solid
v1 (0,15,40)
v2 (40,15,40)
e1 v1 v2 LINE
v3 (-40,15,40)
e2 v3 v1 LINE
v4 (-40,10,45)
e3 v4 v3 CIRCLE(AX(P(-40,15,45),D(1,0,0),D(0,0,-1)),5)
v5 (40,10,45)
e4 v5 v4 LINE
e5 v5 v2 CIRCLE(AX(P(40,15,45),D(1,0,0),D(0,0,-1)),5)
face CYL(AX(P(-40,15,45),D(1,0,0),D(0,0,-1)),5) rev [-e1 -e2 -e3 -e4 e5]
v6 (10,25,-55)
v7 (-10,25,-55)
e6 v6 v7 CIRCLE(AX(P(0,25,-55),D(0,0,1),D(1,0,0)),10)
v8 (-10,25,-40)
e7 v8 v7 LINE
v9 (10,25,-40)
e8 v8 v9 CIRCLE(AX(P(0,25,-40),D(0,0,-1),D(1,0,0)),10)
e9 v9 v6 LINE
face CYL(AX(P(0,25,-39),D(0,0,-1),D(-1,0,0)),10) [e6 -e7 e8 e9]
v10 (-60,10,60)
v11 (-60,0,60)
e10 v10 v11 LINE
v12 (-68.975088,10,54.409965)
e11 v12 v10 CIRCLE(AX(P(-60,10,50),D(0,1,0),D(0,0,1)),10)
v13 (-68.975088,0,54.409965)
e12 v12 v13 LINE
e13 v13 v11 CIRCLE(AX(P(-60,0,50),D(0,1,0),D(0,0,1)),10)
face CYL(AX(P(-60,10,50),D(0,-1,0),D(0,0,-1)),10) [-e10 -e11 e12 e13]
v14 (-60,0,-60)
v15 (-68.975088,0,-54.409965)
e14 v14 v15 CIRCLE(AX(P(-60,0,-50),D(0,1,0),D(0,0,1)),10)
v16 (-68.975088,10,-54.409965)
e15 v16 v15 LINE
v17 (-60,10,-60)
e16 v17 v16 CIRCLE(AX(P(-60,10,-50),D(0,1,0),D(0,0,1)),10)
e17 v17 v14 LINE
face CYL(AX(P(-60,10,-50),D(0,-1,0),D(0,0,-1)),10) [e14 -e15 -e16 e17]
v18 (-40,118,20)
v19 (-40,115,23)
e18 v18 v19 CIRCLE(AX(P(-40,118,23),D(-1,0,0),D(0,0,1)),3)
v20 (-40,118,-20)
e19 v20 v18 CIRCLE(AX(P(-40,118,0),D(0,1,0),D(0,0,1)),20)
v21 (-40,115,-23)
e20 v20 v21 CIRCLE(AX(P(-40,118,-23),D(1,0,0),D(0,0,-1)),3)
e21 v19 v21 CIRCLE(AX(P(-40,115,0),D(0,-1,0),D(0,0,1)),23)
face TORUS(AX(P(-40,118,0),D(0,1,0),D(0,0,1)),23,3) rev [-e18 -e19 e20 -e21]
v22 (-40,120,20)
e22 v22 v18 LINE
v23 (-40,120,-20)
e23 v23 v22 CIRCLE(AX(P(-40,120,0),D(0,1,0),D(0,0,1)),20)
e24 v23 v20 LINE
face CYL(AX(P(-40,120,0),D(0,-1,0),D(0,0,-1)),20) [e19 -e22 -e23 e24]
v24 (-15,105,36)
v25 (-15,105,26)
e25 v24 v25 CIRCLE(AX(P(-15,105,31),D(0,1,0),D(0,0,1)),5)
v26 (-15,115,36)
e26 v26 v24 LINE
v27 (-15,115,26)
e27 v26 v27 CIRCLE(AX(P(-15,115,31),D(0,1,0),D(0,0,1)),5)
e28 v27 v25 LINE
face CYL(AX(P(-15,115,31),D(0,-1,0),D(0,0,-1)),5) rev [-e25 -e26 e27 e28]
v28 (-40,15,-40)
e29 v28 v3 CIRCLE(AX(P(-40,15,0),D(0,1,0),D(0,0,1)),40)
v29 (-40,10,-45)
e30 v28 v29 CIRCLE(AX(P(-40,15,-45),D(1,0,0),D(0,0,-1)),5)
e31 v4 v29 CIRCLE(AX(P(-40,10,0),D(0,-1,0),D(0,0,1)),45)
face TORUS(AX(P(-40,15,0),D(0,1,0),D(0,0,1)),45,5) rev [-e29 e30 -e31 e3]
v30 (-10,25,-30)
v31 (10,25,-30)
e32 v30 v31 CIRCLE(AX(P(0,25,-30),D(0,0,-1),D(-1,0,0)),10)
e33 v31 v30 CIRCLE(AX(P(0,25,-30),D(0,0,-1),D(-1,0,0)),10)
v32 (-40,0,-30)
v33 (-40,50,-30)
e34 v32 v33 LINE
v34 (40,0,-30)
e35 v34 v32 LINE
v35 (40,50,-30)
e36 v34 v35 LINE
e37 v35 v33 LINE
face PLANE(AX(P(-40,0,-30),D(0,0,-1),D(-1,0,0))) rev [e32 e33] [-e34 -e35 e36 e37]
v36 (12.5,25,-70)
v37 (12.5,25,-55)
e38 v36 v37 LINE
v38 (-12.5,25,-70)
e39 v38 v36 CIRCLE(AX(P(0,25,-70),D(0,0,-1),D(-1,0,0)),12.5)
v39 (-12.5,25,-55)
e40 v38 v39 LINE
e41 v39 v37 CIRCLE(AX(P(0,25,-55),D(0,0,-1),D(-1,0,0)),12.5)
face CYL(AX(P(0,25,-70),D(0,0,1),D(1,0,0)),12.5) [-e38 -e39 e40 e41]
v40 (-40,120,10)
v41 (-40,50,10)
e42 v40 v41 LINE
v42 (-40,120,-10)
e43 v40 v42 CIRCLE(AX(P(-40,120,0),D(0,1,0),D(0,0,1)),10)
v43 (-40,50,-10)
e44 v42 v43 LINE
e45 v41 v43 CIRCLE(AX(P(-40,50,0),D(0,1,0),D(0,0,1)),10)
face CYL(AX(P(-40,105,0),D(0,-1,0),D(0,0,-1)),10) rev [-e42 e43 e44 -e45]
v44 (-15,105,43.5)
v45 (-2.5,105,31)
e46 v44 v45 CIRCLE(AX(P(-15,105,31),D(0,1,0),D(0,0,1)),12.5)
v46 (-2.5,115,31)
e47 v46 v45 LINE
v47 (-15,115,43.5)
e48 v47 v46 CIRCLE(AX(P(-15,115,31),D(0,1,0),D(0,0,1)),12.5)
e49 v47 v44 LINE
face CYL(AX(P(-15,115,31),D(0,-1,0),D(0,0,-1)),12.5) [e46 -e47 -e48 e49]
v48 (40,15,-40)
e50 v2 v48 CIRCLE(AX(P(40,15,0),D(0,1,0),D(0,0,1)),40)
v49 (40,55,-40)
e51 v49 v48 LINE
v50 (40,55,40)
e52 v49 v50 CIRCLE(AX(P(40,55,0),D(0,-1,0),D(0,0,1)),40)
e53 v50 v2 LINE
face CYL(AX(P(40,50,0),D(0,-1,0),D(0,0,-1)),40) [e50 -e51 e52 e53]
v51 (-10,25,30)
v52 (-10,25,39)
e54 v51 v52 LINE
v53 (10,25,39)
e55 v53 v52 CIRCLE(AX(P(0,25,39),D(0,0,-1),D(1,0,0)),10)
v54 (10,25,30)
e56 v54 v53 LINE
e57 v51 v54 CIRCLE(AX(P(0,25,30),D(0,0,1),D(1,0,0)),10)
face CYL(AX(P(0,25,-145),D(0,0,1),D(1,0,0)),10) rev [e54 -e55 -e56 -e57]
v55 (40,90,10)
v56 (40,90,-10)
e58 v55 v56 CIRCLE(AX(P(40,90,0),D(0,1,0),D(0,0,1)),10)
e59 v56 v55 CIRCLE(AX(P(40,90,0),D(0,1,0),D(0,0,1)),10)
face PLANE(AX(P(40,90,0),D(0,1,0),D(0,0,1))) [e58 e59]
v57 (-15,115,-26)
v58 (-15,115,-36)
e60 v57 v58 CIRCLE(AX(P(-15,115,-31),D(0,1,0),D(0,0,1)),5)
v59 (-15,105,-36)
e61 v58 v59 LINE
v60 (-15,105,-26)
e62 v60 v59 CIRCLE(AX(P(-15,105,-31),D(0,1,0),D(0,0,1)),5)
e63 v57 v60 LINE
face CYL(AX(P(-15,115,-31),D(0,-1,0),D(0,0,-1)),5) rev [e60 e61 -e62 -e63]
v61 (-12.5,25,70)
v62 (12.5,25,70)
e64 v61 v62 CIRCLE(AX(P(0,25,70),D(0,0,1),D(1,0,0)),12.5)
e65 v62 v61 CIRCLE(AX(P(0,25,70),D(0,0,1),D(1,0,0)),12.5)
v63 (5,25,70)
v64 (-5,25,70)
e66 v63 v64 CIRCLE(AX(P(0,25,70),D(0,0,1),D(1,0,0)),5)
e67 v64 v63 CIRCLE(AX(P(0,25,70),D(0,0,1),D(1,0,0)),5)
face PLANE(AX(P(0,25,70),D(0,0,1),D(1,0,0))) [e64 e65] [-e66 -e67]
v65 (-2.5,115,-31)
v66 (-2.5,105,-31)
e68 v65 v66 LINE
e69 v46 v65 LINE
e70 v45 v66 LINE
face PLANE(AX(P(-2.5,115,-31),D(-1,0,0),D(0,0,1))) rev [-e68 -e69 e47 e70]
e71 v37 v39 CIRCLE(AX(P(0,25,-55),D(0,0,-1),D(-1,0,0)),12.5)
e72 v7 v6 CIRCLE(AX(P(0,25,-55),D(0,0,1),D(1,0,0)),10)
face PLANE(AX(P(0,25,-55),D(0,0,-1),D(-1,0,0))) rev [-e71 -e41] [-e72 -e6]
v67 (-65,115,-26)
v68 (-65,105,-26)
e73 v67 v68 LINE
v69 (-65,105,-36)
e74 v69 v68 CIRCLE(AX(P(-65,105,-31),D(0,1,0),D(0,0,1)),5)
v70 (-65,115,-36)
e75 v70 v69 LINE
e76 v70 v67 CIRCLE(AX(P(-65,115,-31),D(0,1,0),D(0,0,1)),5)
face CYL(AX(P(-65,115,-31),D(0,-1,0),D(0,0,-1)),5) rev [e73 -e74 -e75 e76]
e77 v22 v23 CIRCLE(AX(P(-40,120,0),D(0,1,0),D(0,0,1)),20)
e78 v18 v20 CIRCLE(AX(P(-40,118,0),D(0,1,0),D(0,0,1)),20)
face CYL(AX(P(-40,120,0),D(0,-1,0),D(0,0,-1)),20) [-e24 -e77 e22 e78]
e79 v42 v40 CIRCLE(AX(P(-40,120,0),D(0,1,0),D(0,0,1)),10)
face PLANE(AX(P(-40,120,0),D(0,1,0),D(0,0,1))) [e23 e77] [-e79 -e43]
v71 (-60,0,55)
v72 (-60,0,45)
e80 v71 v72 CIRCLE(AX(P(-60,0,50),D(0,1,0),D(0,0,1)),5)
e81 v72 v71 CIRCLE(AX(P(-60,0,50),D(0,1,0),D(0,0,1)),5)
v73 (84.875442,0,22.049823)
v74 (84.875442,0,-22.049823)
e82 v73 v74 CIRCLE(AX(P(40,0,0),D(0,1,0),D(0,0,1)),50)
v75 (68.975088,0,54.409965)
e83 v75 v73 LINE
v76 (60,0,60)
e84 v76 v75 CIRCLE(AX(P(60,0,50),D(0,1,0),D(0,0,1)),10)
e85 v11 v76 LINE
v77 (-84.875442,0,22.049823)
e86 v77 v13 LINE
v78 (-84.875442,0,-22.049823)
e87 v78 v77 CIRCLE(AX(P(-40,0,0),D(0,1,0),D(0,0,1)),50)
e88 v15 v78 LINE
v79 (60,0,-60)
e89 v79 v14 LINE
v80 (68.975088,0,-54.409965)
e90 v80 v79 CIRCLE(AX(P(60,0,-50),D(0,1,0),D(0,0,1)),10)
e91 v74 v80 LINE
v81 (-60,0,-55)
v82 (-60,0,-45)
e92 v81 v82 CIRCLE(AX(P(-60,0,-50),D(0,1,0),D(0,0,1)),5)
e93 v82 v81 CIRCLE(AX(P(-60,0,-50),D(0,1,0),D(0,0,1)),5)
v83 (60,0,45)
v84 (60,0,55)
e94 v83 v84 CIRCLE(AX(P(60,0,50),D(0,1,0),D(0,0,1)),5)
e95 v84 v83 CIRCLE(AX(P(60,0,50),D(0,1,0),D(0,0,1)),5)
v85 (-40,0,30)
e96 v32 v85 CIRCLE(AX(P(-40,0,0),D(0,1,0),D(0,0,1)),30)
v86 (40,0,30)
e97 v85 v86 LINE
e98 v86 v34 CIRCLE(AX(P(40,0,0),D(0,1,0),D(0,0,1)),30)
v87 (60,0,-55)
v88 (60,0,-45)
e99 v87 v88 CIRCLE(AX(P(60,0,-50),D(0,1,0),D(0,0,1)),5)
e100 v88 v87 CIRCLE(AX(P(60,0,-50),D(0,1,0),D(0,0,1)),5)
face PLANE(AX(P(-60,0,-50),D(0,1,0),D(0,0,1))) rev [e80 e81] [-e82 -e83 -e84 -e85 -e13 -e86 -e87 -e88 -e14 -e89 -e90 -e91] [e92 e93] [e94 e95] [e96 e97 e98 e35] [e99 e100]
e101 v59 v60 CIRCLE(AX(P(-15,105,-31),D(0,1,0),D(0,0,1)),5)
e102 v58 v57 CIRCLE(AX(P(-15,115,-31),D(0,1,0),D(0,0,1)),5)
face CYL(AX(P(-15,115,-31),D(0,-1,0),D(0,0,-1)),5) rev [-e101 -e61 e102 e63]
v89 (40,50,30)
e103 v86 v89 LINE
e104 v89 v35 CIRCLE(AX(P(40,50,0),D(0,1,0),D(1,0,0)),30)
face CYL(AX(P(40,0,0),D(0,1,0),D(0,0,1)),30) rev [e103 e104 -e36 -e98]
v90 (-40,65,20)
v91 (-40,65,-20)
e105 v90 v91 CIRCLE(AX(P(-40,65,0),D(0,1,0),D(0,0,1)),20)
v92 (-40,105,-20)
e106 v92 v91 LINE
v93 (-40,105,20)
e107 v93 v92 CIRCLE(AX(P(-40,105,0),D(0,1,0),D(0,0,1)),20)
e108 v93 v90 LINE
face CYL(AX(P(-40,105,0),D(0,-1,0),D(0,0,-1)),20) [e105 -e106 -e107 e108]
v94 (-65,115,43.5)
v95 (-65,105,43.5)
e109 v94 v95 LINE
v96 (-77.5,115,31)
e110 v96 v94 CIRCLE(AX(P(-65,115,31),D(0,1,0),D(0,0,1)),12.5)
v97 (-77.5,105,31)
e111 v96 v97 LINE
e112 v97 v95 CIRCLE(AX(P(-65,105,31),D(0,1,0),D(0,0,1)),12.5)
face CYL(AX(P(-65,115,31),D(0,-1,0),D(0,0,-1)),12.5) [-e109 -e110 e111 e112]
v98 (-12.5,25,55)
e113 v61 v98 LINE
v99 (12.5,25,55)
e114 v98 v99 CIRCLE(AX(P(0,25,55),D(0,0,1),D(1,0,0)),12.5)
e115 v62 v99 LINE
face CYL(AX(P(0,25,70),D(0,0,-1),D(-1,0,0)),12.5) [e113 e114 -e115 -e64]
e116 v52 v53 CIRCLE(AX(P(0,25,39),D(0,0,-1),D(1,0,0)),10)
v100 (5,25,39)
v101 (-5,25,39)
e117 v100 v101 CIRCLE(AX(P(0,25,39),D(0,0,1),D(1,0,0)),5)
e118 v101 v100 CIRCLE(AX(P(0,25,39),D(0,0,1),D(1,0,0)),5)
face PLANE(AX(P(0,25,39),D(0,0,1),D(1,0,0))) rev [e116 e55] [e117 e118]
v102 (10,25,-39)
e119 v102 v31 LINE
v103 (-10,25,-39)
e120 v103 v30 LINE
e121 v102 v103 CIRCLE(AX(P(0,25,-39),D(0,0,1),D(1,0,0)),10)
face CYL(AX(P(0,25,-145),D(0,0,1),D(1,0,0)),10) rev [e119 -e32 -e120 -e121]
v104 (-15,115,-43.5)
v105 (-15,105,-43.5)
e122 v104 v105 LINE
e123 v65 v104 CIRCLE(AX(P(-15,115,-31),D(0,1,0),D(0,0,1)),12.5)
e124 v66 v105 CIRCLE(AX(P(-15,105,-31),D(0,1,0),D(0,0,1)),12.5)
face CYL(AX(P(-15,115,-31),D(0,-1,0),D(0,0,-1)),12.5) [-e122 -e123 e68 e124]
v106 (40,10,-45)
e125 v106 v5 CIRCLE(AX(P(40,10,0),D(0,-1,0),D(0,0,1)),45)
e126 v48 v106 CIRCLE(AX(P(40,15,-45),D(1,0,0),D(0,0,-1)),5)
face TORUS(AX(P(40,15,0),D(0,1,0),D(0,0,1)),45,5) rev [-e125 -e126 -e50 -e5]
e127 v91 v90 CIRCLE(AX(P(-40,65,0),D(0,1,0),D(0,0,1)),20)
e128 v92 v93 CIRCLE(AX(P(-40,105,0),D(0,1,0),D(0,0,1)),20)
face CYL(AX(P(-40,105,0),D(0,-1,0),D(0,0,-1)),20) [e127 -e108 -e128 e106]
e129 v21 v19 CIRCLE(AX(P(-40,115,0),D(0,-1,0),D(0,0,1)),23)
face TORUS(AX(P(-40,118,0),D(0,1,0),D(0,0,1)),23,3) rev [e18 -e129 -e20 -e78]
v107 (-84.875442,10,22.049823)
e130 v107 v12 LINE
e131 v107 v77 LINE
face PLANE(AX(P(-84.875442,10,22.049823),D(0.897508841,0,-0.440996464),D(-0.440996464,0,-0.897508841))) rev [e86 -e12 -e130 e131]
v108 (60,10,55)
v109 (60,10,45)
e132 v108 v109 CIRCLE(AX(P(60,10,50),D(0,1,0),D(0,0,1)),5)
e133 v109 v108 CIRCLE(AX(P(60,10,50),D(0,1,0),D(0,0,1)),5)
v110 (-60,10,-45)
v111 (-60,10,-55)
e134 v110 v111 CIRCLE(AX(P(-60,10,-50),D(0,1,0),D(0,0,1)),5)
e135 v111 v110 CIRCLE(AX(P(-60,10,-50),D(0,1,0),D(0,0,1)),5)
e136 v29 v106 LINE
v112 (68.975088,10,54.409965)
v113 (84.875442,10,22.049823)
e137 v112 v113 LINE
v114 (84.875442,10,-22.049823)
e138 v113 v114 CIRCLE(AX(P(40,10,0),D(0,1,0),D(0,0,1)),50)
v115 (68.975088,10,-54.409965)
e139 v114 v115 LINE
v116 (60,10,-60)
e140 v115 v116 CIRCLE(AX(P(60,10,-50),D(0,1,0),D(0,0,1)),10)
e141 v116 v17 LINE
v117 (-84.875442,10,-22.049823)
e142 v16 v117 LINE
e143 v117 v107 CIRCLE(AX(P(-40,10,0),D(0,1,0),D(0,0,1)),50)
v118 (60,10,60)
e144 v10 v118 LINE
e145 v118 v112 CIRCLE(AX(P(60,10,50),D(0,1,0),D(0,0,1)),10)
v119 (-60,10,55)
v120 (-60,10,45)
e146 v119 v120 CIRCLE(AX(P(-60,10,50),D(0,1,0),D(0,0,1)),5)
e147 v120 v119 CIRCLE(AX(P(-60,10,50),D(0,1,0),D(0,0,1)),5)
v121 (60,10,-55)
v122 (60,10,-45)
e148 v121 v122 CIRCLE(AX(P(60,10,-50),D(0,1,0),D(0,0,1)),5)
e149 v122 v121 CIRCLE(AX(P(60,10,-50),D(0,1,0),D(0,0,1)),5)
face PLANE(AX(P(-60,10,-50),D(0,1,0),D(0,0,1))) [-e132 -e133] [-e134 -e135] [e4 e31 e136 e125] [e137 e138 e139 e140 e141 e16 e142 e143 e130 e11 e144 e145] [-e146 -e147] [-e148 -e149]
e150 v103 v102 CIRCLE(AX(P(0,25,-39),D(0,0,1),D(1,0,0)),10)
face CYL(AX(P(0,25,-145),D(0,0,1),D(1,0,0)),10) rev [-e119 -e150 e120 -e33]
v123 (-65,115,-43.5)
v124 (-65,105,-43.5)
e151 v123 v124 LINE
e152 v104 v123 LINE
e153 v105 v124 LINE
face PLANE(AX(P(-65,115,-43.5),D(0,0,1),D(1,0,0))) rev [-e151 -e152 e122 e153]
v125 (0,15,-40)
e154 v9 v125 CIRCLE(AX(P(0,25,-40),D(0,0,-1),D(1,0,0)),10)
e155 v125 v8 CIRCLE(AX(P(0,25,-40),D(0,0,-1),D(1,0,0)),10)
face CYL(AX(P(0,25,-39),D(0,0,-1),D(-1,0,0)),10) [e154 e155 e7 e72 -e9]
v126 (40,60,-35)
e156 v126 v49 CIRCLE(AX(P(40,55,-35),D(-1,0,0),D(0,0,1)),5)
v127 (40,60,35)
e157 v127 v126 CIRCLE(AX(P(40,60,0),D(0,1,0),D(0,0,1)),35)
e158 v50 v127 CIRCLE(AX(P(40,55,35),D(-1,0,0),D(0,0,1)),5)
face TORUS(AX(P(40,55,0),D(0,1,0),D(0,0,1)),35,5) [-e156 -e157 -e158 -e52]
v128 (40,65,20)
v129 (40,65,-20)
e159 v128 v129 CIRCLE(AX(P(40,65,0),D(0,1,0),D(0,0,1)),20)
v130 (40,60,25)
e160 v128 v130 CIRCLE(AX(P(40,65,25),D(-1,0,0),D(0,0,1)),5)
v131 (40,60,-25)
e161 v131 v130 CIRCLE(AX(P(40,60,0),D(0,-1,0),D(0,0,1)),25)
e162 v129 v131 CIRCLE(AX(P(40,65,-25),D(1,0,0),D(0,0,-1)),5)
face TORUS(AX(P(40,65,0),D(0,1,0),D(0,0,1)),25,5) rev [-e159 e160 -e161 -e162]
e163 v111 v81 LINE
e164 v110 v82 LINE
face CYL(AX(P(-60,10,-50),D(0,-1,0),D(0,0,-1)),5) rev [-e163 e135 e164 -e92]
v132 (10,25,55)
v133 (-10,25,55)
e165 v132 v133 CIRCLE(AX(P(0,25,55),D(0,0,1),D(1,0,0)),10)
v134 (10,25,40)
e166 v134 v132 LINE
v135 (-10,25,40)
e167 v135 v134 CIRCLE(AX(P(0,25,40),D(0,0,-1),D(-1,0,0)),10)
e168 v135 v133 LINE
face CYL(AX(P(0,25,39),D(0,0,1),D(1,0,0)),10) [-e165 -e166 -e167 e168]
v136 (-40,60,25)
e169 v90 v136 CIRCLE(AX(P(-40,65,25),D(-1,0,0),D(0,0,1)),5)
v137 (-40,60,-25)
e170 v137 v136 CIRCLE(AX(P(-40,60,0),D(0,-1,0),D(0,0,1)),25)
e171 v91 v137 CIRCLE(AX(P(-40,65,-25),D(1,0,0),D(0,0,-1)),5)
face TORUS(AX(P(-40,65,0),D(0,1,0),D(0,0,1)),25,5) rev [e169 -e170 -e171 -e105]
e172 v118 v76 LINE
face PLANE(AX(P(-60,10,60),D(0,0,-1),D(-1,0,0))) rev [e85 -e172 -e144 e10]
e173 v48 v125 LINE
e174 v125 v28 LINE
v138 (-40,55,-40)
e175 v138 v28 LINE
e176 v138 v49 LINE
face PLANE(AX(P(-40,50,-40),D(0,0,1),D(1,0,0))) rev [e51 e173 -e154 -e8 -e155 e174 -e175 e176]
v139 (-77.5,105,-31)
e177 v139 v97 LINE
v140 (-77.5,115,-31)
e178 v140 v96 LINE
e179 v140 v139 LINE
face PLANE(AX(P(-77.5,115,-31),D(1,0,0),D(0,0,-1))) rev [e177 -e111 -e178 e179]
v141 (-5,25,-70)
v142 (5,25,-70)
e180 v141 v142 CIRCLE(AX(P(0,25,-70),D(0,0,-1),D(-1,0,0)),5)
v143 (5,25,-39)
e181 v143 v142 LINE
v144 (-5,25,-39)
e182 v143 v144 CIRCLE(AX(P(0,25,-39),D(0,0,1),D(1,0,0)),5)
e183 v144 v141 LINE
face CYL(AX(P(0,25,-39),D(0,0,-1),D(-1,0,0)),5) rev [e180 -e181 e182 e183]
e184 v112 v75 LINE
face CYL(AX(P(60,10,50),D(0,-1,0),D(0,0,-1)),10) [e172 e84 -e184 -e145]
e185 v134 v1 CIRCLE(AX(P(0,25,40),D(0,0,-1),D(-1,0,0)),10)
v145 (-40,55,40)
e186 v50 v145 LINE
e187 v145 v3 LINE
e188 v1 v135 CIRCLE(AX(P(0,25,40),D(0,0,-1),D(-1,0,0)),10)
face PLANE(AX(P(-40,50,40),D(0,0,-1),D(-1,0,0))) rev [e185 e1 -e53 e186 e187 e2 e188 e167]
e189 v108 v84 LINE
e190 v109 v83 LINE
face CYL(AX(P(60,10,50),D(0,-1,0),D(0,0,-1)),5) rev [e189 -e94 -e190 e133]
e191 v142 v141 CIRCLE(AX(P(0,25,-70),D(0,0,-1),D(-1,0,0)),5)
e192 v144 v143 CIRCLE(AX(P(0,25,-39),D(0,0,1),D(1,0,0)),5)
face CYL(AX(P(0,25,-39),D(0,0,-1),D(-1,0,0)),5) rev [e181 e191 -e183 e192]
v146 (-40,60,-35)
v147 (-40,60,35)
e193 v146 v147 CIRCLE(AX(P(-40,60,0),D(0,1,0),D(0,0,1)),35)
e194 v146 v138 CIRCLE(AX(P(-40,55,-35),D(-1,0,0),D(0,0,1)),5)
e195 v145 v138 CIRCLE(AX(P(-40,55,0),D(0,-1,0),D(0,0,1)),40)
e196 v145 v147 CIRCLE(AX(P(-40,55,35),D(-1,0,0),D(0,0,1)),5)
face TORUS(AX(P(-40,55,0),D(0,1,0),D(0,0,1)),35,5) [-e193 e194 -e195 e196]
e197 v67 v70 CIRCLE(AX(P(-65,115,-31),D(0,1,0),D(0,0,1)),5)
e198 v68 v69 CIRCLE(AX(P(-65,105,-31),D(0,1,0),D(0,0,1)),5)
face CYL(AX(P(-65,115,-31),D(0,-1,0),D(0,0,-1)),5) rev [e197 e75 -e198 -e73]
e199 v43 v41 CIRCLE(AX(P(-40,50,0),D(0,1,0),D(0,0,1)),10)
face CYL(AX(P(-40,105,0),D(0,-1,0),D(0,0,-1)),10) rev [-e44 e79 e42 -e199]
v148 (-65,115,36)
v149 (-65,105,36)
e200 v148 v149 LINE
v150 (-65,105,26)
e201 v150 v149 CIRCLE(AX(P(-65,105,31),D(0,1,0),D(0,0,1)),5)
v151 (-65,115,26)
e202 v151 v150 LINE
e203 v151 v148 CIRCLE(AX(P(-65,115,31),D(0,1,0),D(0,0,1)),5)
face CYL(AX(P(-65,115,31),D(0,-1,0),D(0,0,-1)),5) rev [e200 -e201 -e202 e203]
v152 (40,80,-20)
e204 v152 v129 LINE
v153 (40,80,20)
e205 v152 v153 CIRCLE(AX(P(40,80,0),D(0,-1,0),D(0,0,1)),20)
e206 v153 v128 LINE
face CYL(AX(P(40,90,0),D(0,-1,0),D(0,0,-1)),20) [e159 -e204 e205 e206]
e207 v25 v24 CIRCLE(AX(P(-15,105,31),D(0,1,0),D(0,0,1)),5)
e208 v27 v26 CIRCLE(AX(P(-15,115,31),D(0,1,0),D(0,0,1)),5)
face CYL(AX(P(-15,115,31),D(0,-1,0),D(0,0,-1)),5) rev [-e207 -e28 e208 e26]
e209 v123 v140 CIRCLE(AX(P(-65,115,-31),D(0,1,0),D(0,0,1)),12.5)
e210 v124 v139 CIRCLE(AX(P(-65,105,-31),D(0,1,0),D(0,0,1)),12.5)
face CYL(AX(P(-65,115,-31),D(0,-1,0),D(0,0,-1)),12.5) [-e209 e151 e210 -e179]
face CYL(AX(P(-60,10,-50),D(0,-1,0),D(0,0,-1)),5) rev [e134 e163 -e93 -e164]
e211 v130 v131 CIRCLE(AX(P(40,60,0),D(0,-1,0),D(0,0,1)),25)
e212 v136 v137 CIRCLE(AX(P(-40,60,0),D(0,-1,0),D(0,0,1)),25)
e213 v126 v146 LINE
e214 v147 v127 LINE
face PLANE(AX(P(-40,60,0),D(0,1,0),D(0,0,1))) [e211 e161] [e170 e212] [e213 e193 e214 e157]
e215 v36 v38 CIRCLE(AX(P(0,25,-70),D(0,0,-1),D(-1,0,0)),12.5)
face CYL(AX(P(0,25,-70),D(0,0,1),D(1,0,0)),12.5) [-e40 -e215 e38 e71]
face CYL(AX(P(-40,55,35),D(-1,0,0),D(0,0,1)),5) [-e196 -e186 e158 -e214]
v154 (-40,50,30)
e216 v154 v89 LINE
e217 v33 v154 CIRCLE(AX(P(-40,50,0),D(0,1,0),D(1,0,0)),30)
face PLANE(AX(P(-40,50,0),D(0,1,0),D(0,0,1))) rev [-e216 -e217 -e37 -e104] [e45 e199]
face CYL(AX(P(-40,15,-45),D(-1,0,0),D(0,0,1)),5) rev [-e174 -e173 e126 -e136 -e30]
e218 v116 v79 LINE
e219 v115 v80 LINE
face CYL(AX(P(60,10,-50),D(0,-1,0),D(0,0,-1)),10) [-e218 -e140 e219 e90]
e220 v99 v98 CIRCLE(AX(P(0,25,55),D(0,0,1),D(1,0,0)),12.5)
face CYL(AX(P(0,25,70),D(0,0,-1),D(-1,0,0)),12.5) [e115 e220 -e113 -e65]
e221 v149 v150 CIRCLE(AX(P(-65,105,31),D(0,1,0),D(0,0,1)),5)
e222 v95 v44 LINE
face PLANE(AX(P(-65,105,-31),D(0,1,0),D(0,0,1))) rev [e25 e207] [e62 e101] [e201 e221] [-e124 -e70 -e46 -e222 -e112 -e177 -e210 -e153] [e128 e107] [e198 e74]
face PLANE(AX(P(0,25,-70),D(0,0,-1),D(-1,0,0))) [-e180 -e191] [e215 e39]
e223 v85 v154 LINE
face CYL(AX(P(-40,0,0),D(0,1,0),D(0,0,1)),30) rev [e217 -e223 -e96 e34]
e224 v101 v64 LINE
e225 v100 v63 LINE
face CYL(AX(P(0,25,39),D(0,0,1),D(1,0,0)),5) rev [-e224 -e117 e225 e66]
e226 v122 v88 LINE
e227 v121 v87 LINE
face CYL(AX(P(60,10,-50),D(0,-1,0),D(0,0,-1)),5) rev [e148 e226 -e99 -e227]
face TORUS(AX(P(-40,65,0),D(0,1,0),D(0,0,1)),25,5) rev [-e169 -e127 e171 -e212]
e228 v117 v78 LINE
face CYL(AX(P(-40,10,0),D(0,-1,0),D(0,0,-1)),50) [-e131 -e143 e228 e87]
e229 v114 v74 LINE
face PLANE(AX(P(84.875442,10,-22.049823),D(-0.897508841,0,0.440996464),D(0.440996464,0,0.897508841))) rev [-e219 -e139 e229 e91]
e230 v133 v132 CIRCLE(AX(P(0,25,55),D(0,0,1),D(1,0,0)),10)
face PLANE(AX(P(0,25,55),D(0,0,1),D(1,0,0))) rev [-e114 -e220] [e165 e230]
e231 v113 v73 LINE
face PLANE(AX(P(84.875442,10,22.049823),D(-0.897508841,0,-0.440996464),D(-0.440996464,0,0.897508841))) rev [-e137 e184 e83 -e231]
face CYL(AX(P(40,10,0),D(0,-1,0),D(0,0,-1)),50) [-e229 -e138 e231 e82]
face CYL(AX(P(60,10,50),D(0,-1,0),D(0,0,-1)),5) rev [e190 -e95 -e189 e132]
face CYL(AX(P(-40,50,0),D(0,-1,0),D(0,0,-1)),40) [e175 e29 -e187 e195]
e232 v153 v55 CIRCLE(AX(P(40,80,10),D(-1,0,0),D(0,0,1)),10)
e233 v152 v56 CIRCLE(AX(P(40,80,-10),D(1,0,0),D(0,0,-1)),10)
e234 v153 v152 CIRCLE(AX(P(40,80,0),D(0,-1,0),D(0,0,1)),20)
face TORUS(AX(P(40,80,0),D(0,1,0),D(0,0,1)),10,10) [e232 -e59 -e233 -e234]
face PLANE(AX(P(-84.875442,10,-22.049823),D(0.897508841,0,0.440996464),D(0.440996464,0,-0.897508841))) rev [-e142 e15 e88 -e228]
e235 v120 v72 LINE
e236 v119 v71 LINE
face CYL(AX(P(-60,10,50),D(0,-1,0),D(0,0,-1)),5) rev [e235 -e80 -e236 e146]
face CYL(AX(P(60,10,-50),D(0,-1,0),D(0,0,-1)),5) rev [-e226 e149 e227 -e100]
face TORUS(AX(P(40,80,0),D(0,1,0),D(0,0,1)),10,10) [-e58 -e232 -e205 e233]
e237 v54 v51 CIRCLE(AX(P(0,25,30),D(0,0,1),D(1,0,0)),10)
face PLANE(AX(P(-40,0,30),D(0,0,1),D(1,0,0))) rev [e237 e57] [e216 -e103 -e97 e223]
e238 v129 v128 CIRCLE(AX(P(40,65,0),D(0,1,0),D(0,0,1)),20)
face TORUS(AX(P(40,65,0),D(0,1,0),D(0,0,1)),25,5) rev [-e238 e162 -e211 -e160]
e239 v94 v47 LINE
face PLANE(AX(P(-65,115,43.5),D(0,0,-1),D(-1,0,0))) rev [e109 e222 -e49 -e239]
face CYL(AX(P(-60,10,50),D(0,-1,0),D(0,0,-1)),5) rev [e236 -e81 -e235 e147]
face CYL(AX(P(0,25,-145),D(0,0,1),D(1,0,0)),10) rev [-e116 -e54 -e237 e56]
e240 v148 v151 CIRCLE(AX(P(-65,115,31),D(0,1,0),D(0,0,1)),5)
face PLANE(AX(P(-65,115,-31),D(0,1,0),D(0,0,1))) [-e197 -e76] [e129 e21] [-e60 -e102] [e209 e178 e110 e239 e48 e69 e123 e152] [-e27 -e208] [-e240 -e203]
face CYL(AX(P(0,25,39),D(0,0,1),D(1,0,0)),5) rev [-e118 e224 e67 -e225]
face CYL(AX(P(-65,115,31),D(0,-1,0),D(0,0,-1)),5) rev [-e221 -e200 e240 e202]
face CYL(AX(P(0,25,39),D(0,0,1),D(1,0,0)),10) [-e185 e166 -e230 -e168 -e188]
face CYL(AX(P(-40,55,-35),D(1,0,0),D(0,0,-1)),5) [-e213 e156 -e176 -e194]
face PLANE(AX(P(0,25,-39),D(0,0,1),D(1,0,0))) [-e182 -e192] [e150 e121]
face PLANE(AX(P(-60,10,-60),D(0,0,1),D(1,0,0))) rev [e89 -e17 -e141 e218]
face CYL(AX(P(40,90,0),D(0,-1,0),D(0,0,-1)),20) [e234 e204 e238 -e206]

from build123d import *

# Parameters (mm, degrees)
BASE_FLANGE_SKETCH_R           = 5
BASE_FLANGE_DEPTH              = 10
FLANGE_POCKET_CUT_DEPTH        = 10
HOUSING_START                  = 40
HOUSING_WALL_DEPTH             = 40
HOUSING_START_2                = 10
HOUSING_COVER_DEPTH            = 10
COVER_EDGE_FILLET_R5_R         = 5
SHAFT_BOSS_SKETCH_R            = 20
SHAFT_BOSS_SKETCH_R_2          = 10
SHAFT_BOSS_40_DEPTH            = 45
PLUG_BOSS_SKETCH_R             = 20
PLUG_BOSS_40_DEPTH             = 30
PLUG_BOSS_TOP_FILLET_R10_R     = 10
BOSS_ROOT_FILLETS_R5_R         = 5
SHAFT_START                    = -60
SHAFT_BORE_SKETCH_R            = 10
SHAFT_BORE_20_DEPTH            = 60
TOP_MOUNTING_FLANGE_SKETCH_R   = 5
TOP_MOUNTING_FLANGE_SKETCH_R_2 = 10
TOP_MOUNTING_FLANGE_DEPTH      = 10
TOP_FLANGE_SPIGOT_SKETCH_R     = 20
TOP_FLANGE_SPIGOT_SKETCH_R_2   = 10
TOP_FLANGE_SPIGOT_40_DEPTH     = 5
TOP_FLANGE_FILLET_R3_R         = 3
SIDE_PORT_CUT_SKETCH_R         = 10
SIDE_PORT_CLEARANCE_CUT_DEPTH  = 200
SIDE_PORT_BOSS_A_SKETCH_R      = 10
SIDE_PORT_BOSS_A_SKETCH_R_2    = 5
SIDE_PORT_BOSS_A_DEPTH         = 16
SIDE_START                     = 16
SIDE_PORT_BOSS_B_SKETCH_R      = 10
SIDE_PORT_BOSS_B_SKETCH_R_2    = 5
SIDE_PORT_BOSS_B_DEPTH         = 16
PORT_START                     = 15
PORT_SPIGOT_A_SKETCH_R         = 12.5
PORT_SPIGOT_A_SKETCH_R_2       = 5
PORT_SPIGOT_A_DEPTH            = 15
PORT_SPIGOT_B_SKETCH_R         = 12.5
PORT_SPIGOT_B_SKETCH_R_2       = 5
PORT_SPIGOT_B_DEPTH            = 15


with BuildPart() as part:
    # Base Flange Sketch → Base Flange (new body)
    with BuildSketch(Plane(origin=(0, 0, 0), x_dir=(1, 0, 0), z_dir=(0, 1, 0))):
        with BuildLine():
            Line((-60, 60), (60, 60))
            ThreePointArc((60, 60), (65.286792677, 58.488216726), (68.975088406, 54.409964638))
            Line((68.975088406, 54.409964638), (84.87544203, 22.049823188))
            ThreePointArc((84.87544203, 22.049823188), (90, 0), (84.87544203, -22.049823188))
            Line((84.87544203, -22.049823188), (68.975088406, -54.409964638))
            ThreePointArc((68.975088406, -54.409964638), (65.286792677, -58.488216726), (60, -60))
            Line((60, -60), (-60, -60))
            ThreePointArc((-60, -60), (-65.286792677, -58.488216726), (-68.975088406, -54.409964638))
            Line((-68.975088406, -54.409964638), (-84.87544203, -22.049823188))
            ThreePointArc((-84.87544203, -22.049823188), (-90, 0), (-84.87544203, 22.049823188))
            Line((-84.87544203, 22.049823188), (-68.975088406, 54.409964638))
            ThreePointArc((-68.975088406, 54.409964638), (-65.286792677, 58.488216726), (-60, 60))
        make_face()
        with Locations(Location((-60, 50, 0), (0, 0, 270))):
            Circle(BASE_FLANGE_SKETCH_R, mode=Mode.SUBTRACT)
        with Locations(Location((-60, -50, 0), (0, 0, 270))):
            Circle(BASE_FLANGE_SKETCH_R, mode=Mode.SUBTRACT)
        with Locations(Location((60, 50, 0), (0, 0, 270))):
            Circle(BASE_FLANGE_SKETCH_R, mode=Mode.SUBTRACT)
        with Locations(Location((60, -50, 0), (0, 0, 270))):
            Circle(BASE_FLANGE_SKETCH_R, mode=Mode.SUBTRACT)
    extrude(amount=BASE_FLANGE_DEPTH)

    # Flange Pocket Sketch → Flange Pocket Cut (cut)
    with BuildSketch(Plane(origin=(0, 10, 0), x_dir=(1, 0, 0), z_dir=(0, 1, 0))):
        with BuildLine():
            Line((-40, 30), (40, 30))
            ThreePointArc((40, 30), (70, 0), (40, -30))
            Line((40, -30), (-40, -30))
            ThreePointArc((-40, -30), (-70, 0), (-40, 30))
        make_face()
    extrude(amount=-FLANGE_POCKET_CUT_DEPTH, mode=Mode.SUBTRACT)

    # Housing Wall Sketch → Housing Wall (add)
    with BuildSketch(Plane(origin=(0, 10, 0), x_dir=(1, 0, 0), z_dir=(0, 1, 0)).offset(HOUSING_START)):
        with BuildLine():
            Line((40, -40), (-40, -40))
            ThreePointArc((-40, -40), (-80, 0), (-40, 40))
            Line((-40, 40), (40, 40))
            ThreePointArc((40, 40), (80, 0), (40, -40))
        make_face()
        with BuildLine():
            Line((40, -30), (-40, -30))
            ThreePointArc((-40, -30), (-70, 0), (-40, 30))
            Line((-40, 30), (40, 30))
            ThreePointArc((40, 30), (70, 0), (40, -30))
        make_face(mode=Mode.SUBTRACT)
    extrude(amount=-HOUSING_WALL_DEPTH)

    # Housing Cover Sketch → Housing Cover (add)
    with BuildSketch(Plane(origin=(0, 50, 0), x_dir=(1, 0, 0), z_dir=(0, 1, 0)).offset(HOUSING_START_2)):
        with BuildLine():
            Line((-40, 40), (40, 40))
            ThreePointArc((40, 40), (80, 0), (40, -40))
            Line((40, -40), (-40, -40))
            ThreePointArc((-40, -40), (-80, 0), (-40, 40))
        make_face()
    extrude(amount=-HOUSING_COVER_DEPTH)

    # Cover Edge Fillet R5
    cover_edge_fillet_r5_edges = [part.edges().sort_by_distance(p)[0] for p in [
        (-80, 10, 0),
        (0, 10, 40),
        (80, 10, 0),
        (0, 10, -40),
        (-80, 60, 0),
        (0, 60, 40),
        (80, 60, 0),
        (0, 60, -40),
    ]]
    fillet(cover_edge_fillet_r5_edges, radius=COVER_EDGE_FILLET_R5_R)

    # Shaft Boss Sketch → Shaft Boss Ø40 (add)
    with BuildSketch(Plane(origin=(0, 60, 0), x_dir=(1, 0, 0), z_dir=(0, 1, 0))):
        with Locations(Location((-40, 0, 0), (0, 0, 90))):
            Circle(SHAFT_BOSS_SKETCH_R)
        with Locations(Location((-40, 0, 0), (0, 0, 90))):
            Circle(SHAFT_BOSS_SKETCH_R_2, mode=Mode.SUBTRACT)
    extrude(amount=SHAFT_BOSS_40_DEPTH)

    # Plug Boss Sketch → Plug Boss Ø40 (add)
    with BuildSketch(Plane(origin=(0, 60, 0), x_dir=(1, 0, 0), z_dir=(0, 1, 0))):
        with Locations(Location((40, 0, 0), (0, 0, 270))):
            Circle(PLUG_BOSS_SKETCH_R)
    extrude(amount=PLUG_BOSS_40_DEPTH)

    # Plug Boss Top Fillet R10
    plug_boss_top_fillet_r10_edges = [part.edges().sort_by_distance(p)[0] for p in [
        (40, 90, -20),
    ]]
    fillet(plug_boss_top_fillet_r10_edges, radius=PLUG_BOSS_TOP_FILLET_R10_R)

    # Boss Root Fillets R5
    boss_root_fillets_r5_edges = [part.edges().sort_by_distance(p)[0] for p in [
        (-40, 60, 20),
        (40, 60, -20),
    ]]
    fillet(boss_root_fillets_r5_edges, radius=BOSS_ROOT_FILLETS_R5_R)

    # Shaft Bore Sketch → Shaft Bore Ø20 (cut)
    with BuildSketch(Plane(origin=(0, 105, 0), x_dir=(1, 0, 0), z_dir=(0, 1, 0)).offset(SHAFT_START)):
        with Locations(Location((-40, 0, 0), (0, 0, 90))):
            Circle(SHAFT_BORE_SKETCH_R)
    extrude(amount=SHAFT_BORE_20_DEPTH, mode=Mode.SUBTRACT)

    # Top Mounting Flange Sketch → Top Mounting Flange (add)
    with BuildSketch(Plane(origin=(0, 105, 0), x_dir=(1, 0, 0), z_dir=(0, 1, 0))):
        with BuildLine():
            Line((-65, 43.5), (-15, 43.5))
            ThreePointArc((-15, 43.5), (-6.161165235, 39.838834765), (-2.5, 31))
            Line((-2.5, 31), (-2.5, -31))
            ThreePointArc((-2.5, -31), (-6.161165235, -39.838834765), (-15, -43.5))
            Line((-15, -43.5), (-65, -43.5))
            ThreePointArc((-65, -43.5), (-73.838834765, -39.838834765), (-77.5, -31))
            Line((-77.5, -31), (-77.5, 31))
            ThreePointArc((-77.5, 31), (-73.838834765, 39.838834765), (-65, 43.5))
        make_face()
        with Locations(Location((-65, 31, 0), (0, 0, 270))):
            Circle(TOP_MOUNTING_FLANGE_SKETCH_R, mode=Mode.SUBTRACT)
        with Locations(Location((-15, 31, 0), (0, 0, 270))):
            Circle(TOP_MOUNTING_FLANGE_SKETCH_R, mode=Mode.SUBTRACT)
        with Locations(Location((-65, -31, 0), (0, 0, 270))):
            Circle(TOP_MOUNTING_FLANGE_SKETCH_R, mode=Mode.SUBTRACT)
        with Locations(Location((-15, -31, 0), (0, 0, 270))):
            Circle(TOP_MOUNTING_FLANGE_SKETCH_R, mode=Mode.SUBTRACT)
        with Locations(Location((-40, 0, 0), (0, 0, 90))):
            Circle(TOP_MOUNTING_FLANGE_SKETCH_R_2, mode=Mode.SUBTRACT)
    extrude(amount=TOP_MOUNTING_FLANGE_DEPTH)

    # Top Flange Spigot Sketch → Top Flange Spigot Ø40 (add)
    with BuildSketch(Plane(origin=(0, 115, 0), x_dir=(1, 0, 0), z_dir=(0, 1, 0))):
        with Locations(Location((-40, 0, 0), (0, 0, 90))):
            Circle(TOP_FLANGE_SPIGOT_SKETCH_R)
        with Locations(Location((-40, 0, 0), (0, 0, 90))):
            Circle(TOP_FLANGE_SPIGOT_SKETCH_R_2, mode=Mode.SUBTRACT)
    extrude(amount=TOP_FLANGE_SPIGOT_40_DEPTH)

    # Top Flange Fillet R3
    top_flange_fillet_r3_edges = [part.edges().sort_by_distance(p)[0] for p in [
        (-40, 115, 20),
    ]]
    fillet(top_flange_fillet_r3_edges, radius=TOP_FLANGE_FILLET_R3_R)

    # Side Port Cut Sketch → Side Port Clearance Cut (cut)
    with BuildSketch(Plane.XY.offset(55)):
        with Locations(Location((0, 25, 0), (0, 0, 270))):
            Circle(SIDE_PORT_CUT_SKETCH_R)
    extrude(amount=-SIDE_PORT_CLEARANCE_CUT_DEPTH, mode=Mode.SUBTRACT)

    # Side Port Boss A Sketch → Side Port Boss A (add)
    with BuildSketch(Plane.XY.offset(55)):
        with Locations((0, 25)):
            Circle(SIDE_PORT_BOSS_A_SKETCH_R)
        with Locations((0, 25)):
            Circle(SIDE_PORT_BOSS_A_SKETCH_R_2, mode=Mode.SUBTRACT)
    extrude(amount=-SIDE_PORT_BOSS_A_DEPTH)

    # Side Port Boss B Sketch → Side Port Boss B (add)
    with BuildSketch(Plane.XY.offset(-55).offset(SIDE_START)):
        with Locations((0, 25)):
            Circle(SIDE_PORT_BOSS_B_SKETCH_R)
        with Locations((0, 25)):
            Circle(SIDE_PORT_BOSS_B_SKETCH_R_2, mode=Mode.SUBTRACT)
    extrude(amount=-SIDE_PORT_BOSS_B_DEPTH)

    # Port Spigot A Sketch → Port Spigot A (add)
    with BuildSketch(Plane.XY.offset(55).offset(PORT_START)):
        with Locations((0, 25)):
            Circle(PORT_SPIGOT_A_SKETCH_R)
        with Locations((0, 25)):
            Circle(PORT_SPIGOT_A_SKETCH_R_2, mode=Mode.SUBTRACT)
    extrude(amount=-PORT_SPIGOT_A_DEPTH)

    # Port Spigot B Sketch → Port Spigot B (add)
    with BuildSketch(Plane(origin=(0, 0, -55), x_dir=(-1, 0, 0), z_dir=(0, 0, -1))):
        with Locations(Location((0, 25, 0), (0, 0, 180))):
            Circle(PORT_SPIGOT_B_SKETCH_R)
        with Locations(Location((0, 25, 0), (0, 0, 180))):
            Circle(PORT_SPIGOT_B_SKETCH_R_2, mode=Mode.SUBTRACT)
    extrude(amount=PORT_SPIGOT_B_DEPTH)


solid = part.part
